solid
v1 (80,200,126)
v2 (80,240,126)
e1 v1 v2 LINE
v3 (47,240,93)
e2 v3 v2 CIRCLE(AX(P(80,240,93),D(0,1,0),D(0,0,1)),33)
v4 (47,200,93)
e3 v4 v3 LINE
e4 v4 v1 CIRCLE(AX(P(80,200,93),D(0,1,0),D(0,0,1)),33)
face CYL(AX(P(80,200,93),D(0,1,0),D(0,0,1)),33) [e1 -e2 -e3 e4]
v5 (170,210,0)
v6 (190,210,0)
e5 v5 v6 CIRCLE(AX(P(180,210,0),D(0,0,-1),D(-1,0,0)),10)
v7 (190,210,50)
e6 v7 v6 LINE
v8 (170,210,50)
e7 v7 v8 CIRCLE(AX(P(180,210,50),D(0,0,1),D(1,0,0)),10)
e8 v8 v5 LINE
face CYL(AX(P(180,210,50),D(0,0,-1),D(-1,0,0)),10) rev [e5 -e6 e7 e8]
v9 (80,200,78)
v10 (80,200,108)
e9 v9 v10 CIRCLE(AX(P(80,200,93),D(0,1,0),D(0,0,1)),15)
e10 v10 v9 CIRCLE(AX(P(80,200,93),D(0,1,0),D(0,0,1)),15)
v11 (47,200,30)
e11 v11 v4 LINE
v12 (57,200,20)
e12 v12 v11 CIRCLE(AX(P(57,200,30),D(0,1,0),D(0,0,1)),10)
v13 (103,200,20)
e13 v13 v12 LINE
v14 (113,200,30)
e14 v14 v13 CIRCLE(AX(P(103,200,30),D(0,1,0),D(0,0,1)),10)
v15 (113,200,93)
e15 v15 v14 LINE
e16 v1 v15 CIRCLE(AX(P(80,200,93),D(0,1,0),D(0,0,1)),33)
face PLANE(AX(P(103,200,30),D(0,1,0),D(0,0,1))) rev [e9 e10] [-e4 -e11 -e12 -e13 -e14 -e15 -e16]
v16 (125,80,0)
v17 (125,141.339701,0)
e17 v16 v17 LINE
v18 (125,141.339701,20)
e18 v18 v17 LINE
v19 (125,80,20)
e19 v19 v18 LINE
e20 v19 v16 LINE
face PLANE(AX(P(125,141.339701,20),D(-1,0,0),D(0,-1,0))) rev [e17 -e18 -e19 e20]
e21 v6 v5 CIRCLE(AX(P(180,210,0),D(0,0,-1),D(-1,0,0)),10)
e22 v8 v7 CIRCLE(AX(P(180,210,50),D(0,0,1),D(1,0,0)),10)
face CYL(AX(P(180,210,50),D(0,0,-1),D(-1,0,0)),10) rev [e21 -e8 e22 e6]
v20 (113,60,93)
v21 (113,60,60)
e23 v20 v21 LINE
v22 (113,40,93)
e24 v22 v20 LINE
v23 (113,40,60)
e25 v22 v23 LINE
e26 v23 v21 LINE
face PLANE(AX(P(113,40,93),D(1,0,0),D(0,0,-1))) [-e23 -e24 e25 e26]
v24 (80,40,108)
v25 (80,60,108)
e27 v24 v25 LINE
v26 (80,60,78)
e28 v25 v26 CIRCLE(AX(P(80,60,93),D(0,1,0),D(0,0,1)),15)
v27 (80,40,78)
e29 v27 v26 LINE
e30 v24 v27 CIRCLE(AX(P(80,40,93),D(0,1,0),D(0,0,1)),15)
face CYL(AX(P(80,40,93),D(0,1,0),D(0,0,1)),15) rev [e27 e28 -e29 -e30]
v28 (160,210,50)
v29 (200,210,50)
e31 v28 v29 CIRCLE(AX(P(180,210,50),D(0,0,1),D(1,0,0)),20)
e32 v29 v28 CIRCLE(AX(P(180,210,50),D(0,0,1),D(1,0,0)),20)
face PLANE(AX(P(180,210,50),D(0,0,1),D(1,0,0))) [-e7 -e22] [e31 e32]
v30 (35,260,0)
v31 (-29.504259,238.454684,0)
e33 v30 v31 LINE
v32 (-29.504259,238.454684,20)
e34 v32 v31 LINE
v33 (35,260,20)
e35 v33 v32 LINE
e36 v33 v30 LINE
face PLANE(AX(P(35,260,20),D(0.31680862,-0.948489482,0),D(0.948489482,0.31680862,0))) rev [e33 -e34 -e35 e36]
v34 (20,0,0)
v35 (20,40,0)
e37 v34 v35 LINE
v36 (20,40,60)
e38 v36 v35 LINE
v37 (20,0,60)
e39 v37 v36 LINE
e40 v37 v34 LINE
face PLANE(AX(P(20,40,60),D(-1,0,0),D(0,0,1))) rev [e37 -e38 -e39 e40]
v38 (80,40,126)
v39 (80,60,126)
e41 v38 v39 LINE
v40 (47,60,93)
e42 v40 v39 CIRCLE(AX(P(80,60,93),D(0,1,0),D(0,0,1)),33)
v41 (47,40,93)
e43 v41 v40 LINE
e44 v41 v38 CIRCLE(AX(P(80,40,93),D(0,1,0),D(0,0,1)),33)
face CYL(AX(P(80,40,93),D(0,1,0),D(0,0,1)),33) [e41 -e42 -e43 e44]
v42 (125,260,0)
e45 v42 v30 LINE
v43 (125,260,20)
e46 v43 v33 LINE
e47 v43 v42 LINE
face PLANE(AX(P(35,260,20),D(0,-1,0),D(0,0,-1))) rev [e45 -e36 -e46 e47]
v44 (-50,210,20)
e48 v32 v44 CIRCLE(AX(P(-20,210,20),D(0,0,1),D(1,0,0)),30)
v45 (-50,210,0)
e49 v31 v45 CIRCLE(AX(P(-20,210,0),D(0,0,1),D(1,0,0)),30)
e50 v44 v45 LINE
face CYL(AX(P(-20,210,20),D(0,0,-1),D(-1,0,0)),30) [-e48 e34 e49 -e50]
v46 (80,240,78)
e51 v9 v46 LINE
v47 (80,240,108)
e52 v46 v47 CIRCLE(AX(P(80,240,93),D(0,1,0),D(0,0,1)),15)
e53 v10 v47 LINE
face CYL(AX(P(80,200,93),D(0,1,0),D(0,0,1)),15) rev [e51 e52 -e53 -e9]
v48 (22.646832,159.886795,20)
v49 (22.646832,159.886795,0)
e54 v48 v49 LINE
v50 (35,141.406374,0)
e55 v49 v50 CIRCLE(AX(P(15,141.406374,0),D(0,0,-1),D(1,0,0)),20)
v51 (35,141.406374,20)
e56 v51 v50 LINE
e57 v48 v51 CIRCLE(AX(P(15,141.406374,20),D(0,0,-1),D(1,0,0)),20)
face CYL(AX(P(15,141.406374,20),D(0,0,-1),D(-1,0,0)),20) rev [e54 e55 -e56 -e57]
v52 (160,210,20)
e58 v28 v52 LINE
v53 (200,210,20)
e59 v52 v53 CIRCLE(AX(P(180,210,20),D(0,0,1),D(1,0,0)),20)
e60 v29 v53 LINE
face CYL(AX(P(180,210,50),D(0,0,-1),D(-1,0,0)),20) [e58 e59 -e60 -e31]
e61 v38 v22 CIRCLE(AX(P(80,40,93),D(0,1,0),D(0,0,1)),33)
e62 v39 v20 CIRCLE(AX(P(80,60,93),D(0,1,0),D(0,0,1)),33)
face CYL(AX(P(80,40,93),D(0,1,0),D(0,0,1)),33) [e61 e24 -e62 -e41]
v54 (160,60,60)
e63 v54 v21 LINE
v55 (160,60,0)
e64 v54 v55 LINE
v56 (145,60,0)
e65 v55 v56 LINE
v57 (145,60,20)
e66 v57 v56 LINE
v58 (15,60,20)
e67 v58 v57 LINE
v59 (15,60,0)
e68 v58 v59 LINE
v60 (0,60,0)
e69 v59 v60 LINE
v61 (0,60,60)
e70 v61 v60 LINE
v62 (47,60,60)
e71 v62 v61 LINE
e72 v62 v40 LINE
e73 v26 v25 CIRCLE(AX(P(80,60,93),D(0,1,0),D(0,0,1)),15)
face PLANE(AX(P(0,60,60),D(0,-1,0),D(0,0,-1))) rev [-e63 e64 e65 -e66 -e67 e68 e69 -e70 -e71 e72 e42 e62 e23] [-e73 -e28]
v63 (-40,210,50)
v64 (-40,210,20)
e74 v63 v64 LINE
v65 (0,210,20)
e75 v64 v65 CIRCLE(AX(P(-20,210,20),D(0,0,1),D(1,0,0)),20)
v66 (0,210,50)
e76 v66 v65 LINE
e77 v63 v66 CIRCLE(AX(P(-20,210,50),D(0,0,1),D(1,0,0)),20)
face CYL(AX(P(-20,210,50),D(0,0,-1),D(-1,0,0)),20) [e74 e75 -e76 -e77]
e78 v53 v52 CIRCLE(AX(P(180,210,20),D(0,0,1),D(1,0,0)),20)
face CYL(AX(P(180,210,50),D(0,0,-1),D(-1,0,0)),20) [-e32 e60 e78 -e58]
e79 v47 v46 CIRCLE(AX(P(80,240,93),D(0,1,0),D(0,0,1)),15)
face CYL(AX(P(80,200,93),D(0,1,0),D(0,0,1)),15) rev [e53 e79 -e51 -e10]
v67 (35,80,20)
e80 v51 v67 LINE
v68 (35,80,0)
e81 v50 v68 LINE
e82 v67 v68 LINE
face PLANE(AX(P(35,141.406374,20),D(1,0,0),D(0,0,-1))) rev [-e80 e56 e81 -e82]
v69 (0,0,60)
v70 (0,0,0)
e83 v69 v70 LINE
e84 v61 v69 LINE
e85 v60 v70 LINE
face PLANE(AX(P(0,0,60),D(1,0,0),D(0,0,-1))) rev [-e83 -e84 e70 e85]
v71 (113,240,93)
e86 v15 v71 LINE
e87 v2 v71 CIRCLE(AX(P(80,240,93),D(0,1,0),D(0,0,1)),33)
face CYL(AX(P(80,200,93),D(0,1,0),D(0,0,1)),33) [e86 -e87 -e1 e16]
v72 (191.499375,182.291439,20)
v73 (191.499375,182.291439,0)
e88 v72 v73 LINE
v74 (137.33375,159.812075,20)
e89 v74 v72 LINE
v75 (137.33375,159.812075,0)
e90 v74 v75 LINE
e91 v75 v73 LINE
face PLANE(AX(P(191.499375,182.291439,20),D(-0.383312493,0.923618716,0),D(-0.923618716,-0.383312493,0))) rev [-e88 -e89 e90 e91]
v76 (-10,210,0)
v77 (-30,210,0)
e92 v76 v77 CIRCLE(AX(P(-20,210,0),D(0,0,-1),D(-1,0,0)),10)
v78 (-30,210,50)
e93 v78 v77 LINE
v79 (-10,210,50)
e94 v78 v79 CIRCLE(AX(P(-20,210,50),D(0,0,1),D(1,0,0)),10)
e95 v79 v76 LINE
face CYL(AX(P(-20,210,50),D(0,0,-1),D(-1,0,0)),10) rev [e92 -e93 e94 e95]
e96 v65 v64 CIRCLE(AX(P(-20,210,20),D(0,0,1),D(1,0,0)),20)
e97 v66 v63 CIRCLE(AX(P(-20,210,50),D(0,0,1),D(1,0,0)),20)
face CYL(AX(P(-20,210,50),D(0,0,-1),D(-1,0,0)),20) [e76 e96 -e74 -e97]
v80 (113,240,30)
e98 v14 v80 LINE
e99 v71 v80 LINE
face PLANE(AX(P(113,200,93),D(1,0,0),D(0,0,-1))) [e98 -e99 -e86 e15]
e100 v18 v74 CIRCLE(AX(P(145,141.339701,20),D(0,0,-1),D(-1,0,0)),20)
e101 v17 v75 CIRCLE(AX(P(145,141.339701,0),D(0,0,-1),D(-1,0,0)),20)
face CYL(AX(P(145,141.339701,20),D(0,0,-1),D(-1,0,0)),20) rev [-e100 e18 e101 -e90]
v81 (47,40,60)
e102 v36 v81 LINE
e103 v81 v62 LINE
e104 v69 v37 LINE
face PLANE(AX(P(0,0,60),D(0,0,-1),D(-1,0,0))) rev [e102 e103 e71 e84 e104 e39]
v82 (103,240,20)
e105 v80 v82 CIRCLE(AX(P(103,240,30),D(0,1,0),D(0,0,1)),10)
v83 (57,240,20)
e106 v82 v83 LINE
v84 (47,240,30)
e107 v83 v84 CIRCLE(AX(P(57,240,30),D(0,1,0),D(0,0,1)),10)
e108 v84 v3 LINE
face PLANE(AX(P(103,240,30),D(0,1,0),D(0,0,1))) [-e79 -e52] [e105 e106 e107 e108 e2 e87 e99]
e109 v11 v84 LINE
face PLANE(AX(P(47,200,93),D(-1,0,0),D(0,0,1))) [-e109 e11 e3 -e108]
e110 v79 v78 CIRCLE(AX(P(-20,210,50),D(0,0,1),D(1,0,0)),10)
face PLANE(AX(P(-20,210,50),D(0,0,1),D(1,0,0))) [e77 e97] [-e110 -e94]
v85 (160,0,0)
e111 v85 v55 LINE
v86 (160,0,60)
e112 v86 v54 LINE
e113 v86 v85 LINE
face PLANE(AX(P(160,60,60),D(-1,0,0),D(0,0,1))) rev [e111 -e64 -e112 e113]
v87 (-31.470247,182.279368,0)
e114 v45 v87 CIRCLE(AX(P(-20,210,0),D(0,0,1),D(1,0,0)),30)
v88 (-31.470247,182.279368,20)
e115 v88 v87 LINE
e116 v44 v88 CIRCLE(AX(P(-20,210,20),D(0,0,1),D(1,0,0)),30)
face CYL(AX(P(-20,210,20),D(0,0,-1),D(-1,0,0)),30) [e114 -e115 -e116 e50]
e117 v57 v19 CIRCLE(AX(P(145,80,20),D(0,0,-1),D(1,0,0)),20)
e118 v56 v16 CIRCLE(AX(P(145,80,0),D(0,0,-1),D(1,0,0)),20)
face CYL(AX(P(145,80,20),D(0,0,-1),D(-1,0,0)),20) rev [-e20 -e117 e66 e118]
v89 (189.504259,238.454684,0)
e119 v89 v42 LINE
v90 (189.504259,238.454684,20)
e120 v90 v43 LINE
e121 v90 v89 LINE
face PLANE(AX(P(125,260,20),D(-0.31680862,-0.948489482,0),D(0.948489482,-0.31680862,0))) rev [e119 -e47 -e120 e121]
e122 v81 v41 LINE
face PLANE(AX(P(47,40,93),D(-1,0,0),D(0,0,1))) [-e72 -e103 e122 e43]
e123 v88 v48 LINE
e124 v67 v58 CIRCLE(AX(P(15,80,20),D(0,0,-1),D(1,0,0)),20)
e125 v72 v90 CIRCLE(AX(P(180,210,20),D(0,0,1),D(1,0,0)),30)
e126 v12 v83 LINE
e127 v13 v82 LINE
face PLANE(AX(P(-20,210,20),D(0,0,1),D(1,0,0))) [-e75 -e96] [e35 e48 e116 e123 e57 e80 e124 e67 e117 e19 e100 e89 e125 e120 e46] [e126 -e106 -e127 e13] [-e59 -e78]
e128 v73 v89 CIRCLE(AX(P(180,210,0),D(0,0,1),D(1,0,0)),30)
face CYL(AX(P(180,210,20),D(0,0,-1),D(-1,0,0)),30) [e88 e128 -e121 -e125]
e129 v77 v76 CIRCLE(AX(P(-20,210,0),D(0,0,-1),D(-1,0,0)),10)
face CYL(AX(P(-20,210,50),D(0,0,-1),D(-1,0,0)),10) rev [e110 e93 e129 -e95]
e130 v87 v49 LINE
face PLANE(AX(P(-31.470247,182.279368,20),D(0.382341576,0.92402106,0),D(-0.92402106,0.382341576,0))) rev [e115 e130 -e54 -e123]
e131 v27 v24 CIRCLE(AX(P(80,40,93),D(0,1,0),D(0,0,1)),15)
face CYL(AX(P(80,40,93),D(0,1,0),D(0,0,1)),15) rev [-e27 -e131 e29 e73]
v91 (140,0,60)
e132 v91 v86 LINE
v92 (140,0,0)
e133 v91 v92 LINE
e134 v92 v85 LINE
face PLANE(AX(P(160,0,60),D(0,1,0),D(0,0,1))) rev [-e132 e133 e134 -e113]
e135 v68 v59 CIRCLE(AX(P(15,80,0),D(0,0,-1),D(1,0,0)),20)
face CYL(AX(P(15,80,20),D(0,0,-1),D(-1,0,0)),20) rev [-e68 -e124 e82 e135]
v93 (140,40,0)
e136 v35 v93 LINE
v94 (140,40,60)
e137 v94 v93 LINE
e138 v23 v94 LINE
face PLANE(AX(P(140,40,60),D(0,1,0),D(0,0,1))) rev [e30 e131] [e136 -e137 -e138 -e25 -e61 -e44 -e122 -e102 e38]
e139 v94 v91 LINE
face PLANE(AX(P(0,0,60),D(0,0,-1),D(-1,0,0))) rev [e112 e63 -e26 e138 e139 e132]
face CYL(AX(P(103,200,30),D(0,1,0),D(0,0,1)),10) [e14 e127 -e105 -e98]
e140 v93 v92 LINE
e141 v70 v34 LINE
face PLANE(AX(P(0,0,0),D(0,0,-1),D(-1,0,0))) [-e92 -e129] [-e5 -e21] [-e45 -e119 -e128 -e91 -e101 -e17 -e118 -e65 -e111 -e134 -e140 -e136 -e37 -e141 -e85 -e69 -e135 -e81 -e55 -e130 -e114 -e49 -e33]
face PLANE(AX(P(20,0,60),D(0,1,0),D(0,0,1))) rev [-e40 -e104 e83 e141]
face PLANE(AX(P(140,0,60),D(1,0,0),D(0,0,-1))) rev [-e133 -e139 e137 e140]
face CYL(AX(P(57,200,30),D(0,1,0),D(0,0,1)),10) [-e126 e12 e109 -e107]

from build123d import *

# Parameters (mm, degrees)
BASE_WEB_DEPTH             = 60
UPPER_LUG_DEPTH            = 20
UPPER_LUG_BORE_SKETCH_R    = 15
UPPER_LUG_BORE_30_DEPTH    = 20
MOUNTING_FLANGE_DEPTH      = 20
FLANGE_BOSSES_SKETCH_R     = 20
FLANGE_BOSSES_SKETCH_R_2   = 10
FLANGE_BOSSES_DEPTH        = 30
LOWER_LUG_SKETCH_R         = 15
LOWER_LUG_DEPTH            = 40
FLANGE_START               = -40
FLANGE_BOSS_HOLES_SKETCH_R = 10
FLANGE_BOSS_HOLES_DEPTH    = 40


with BuildPart() as part:
    # Base Web Sketch → Base Web (new body)
    with BuildSketch(Plane.XY):
        Polygon((0, 0), (0, 60), (160, 60), (160, 0), (140, 0), (140, 40), (20, 40), (20, 0), align=None)
    extrude(amount=BASE_WEB_DEPTH)

    # Upper Lug Sketch → Upper Lug (add)
    with BuildSketch(Plane(origin=(0, 60, 0), x_dir=(1, 0, 0), z_dir=(0, 1, 0))):
        with BuildLine():
            Line((47, -93), (47, -60))
            Line((47, -60), (113, -60))
            Line((113, -60), (113, -93))
            ThreePointArc((113, -93), (80, -126), (47, -93))
        make_face()
    extrude(amount=-UPPER_LUG_DEPTH)

    # Upper Lug Bore Sketch → Upper Lug Bore Ø30 (cut)
    with BuildSketch(Plane(origin=(0, 60, 0), x_dir=(1, 0, 0), z_dir=(0, 1, 0))):
        with Locations(Location((80, -93, 0), (0, 0, 270))):
            Circle(UPPER_LUG_BORE_SKETCH_R)
    extrude(amount=-UPPER_LUG_BORE_30_DEPTH, mode=Mode.SUBTRACT)

    # Mounting Flange Sketch → Mounting Flange (add)
    with BuildSketch(Plane.XY):
        with BuildLine():
            Line((15, 60), (145, 60))
            ThreePointArc((145, 60), (130.857864376, 65.857864376), (125, 80))
            Line((125, 80), (125, 141.339700933))
            ThreePointArc((125, 141.339700933), (128.366825359, 152.445442752), (137.333750135, 159.812075252))
            Line((137.333750135, 159.812075252), (191.499374797, 182.29143852))
            ThreePointArc((191.499374797, 182.29143852), (209.981089089, 211.065033817), (189.504258609, 238.45468447))
            Line((189.504258609, 238.45468447), (125, 260))
            Line((125, 260), (35, 260))
            Line((35, 260), (-29.504258609, 238.45468447))
            ThreePointArc((-29.504258609, 238.45468447), (-49.981644615, 211.049278887), (-31.470247269, 182.279368197))
            Line((-31.470247269, 182.279368197), (22.646831513, 159.886795057))
            ThreePointArc((22.646831513, 159.886795057), (31.627336381, 152.520854718), (35, 141.406373855))
            Line((35, 141.406373855), (35, 80))
            ThreePointArc((35, 80), (29.142135624, 65.857864376), (15, 60))
        make_face()
    extrude(amount=MOUNTING_FLANGE_DEPTH)

    # Flange Bosses Sketch → Flange Bosses (add)
    # profile 1 of 2: a face of its own
    with BuildSketch(Plane.XY.offset(20)):
        with Locations((-20, 210)):
            Circle(FLANGE_BOSSES_SKETCH_R)
        with Locations((-20, 210)):
            Circle(FLANGE_BOSSES_SKETCH_R_2, mode=Mode.SUBTRACT)
    # profile 2 of 2: a face of its own
    with BuildSketch(Plane.XY.offset(20)):
        with Locations((180, 210)):
            Circle(FLANGE_BOSSES_SKETCH_R)
        with Locations((180, 210)):
            Circle(FLANGE_BOSSES_SKETCH_R_2, mode=Mode.SUBTRACT)
    extrude(amount=FLANGE_BOSSES_DEPTH)

    # Lower Lug Sketch → Lower Lug (add)
    with BuildSketch(Plane(origin=(0, 240, 0), x_dir=(1, 0, 0), z_dir=(0, 1, 0))):
        with BuildLine():
            Line((47, -93), (47, -30))
            ThreePointArc((47, -30), (49.928932188, -22.928932188), (57, -20))
            Line((57, -20), (103, -20))
            ThreePointArc((103, -20), (110.071067812, -22.928932188), (113, -30))
            Line((113, -30), (113, -93))
            ThreePointArc((113, -93), (80, -126), (47, -93))
        make_face()
        with Locations(Location((80, -93, 0), (0, 0, 270))):
            Circle(LOWER_LUG_SKETCH_R, mode=Mode.SUBTRACT)
    extrude(amount=-LOWER_LUG_DEPTH)

    # Flange Boss Holes Sketch → Flange Boss Holes (cut)
    with BuildSketch(Plane.XY.offset(20).offset(FLANGE_START)):
        with Locations(Location((-20, 210, 0), (0, 0, 180))):
            Circle(FLANGE_BOSS_HOLES_SKETCH_R)
        with Locations(Location((180, 210, 0), (0, 0, 180))):
            Circle(FLANGE_BOSS_HOLES_SKETCH_R)
    extrude(amount=FLANGE_BOSS_HOLES_DEPTH, mode=Mode.SUBTRACT)


solid = part.part
